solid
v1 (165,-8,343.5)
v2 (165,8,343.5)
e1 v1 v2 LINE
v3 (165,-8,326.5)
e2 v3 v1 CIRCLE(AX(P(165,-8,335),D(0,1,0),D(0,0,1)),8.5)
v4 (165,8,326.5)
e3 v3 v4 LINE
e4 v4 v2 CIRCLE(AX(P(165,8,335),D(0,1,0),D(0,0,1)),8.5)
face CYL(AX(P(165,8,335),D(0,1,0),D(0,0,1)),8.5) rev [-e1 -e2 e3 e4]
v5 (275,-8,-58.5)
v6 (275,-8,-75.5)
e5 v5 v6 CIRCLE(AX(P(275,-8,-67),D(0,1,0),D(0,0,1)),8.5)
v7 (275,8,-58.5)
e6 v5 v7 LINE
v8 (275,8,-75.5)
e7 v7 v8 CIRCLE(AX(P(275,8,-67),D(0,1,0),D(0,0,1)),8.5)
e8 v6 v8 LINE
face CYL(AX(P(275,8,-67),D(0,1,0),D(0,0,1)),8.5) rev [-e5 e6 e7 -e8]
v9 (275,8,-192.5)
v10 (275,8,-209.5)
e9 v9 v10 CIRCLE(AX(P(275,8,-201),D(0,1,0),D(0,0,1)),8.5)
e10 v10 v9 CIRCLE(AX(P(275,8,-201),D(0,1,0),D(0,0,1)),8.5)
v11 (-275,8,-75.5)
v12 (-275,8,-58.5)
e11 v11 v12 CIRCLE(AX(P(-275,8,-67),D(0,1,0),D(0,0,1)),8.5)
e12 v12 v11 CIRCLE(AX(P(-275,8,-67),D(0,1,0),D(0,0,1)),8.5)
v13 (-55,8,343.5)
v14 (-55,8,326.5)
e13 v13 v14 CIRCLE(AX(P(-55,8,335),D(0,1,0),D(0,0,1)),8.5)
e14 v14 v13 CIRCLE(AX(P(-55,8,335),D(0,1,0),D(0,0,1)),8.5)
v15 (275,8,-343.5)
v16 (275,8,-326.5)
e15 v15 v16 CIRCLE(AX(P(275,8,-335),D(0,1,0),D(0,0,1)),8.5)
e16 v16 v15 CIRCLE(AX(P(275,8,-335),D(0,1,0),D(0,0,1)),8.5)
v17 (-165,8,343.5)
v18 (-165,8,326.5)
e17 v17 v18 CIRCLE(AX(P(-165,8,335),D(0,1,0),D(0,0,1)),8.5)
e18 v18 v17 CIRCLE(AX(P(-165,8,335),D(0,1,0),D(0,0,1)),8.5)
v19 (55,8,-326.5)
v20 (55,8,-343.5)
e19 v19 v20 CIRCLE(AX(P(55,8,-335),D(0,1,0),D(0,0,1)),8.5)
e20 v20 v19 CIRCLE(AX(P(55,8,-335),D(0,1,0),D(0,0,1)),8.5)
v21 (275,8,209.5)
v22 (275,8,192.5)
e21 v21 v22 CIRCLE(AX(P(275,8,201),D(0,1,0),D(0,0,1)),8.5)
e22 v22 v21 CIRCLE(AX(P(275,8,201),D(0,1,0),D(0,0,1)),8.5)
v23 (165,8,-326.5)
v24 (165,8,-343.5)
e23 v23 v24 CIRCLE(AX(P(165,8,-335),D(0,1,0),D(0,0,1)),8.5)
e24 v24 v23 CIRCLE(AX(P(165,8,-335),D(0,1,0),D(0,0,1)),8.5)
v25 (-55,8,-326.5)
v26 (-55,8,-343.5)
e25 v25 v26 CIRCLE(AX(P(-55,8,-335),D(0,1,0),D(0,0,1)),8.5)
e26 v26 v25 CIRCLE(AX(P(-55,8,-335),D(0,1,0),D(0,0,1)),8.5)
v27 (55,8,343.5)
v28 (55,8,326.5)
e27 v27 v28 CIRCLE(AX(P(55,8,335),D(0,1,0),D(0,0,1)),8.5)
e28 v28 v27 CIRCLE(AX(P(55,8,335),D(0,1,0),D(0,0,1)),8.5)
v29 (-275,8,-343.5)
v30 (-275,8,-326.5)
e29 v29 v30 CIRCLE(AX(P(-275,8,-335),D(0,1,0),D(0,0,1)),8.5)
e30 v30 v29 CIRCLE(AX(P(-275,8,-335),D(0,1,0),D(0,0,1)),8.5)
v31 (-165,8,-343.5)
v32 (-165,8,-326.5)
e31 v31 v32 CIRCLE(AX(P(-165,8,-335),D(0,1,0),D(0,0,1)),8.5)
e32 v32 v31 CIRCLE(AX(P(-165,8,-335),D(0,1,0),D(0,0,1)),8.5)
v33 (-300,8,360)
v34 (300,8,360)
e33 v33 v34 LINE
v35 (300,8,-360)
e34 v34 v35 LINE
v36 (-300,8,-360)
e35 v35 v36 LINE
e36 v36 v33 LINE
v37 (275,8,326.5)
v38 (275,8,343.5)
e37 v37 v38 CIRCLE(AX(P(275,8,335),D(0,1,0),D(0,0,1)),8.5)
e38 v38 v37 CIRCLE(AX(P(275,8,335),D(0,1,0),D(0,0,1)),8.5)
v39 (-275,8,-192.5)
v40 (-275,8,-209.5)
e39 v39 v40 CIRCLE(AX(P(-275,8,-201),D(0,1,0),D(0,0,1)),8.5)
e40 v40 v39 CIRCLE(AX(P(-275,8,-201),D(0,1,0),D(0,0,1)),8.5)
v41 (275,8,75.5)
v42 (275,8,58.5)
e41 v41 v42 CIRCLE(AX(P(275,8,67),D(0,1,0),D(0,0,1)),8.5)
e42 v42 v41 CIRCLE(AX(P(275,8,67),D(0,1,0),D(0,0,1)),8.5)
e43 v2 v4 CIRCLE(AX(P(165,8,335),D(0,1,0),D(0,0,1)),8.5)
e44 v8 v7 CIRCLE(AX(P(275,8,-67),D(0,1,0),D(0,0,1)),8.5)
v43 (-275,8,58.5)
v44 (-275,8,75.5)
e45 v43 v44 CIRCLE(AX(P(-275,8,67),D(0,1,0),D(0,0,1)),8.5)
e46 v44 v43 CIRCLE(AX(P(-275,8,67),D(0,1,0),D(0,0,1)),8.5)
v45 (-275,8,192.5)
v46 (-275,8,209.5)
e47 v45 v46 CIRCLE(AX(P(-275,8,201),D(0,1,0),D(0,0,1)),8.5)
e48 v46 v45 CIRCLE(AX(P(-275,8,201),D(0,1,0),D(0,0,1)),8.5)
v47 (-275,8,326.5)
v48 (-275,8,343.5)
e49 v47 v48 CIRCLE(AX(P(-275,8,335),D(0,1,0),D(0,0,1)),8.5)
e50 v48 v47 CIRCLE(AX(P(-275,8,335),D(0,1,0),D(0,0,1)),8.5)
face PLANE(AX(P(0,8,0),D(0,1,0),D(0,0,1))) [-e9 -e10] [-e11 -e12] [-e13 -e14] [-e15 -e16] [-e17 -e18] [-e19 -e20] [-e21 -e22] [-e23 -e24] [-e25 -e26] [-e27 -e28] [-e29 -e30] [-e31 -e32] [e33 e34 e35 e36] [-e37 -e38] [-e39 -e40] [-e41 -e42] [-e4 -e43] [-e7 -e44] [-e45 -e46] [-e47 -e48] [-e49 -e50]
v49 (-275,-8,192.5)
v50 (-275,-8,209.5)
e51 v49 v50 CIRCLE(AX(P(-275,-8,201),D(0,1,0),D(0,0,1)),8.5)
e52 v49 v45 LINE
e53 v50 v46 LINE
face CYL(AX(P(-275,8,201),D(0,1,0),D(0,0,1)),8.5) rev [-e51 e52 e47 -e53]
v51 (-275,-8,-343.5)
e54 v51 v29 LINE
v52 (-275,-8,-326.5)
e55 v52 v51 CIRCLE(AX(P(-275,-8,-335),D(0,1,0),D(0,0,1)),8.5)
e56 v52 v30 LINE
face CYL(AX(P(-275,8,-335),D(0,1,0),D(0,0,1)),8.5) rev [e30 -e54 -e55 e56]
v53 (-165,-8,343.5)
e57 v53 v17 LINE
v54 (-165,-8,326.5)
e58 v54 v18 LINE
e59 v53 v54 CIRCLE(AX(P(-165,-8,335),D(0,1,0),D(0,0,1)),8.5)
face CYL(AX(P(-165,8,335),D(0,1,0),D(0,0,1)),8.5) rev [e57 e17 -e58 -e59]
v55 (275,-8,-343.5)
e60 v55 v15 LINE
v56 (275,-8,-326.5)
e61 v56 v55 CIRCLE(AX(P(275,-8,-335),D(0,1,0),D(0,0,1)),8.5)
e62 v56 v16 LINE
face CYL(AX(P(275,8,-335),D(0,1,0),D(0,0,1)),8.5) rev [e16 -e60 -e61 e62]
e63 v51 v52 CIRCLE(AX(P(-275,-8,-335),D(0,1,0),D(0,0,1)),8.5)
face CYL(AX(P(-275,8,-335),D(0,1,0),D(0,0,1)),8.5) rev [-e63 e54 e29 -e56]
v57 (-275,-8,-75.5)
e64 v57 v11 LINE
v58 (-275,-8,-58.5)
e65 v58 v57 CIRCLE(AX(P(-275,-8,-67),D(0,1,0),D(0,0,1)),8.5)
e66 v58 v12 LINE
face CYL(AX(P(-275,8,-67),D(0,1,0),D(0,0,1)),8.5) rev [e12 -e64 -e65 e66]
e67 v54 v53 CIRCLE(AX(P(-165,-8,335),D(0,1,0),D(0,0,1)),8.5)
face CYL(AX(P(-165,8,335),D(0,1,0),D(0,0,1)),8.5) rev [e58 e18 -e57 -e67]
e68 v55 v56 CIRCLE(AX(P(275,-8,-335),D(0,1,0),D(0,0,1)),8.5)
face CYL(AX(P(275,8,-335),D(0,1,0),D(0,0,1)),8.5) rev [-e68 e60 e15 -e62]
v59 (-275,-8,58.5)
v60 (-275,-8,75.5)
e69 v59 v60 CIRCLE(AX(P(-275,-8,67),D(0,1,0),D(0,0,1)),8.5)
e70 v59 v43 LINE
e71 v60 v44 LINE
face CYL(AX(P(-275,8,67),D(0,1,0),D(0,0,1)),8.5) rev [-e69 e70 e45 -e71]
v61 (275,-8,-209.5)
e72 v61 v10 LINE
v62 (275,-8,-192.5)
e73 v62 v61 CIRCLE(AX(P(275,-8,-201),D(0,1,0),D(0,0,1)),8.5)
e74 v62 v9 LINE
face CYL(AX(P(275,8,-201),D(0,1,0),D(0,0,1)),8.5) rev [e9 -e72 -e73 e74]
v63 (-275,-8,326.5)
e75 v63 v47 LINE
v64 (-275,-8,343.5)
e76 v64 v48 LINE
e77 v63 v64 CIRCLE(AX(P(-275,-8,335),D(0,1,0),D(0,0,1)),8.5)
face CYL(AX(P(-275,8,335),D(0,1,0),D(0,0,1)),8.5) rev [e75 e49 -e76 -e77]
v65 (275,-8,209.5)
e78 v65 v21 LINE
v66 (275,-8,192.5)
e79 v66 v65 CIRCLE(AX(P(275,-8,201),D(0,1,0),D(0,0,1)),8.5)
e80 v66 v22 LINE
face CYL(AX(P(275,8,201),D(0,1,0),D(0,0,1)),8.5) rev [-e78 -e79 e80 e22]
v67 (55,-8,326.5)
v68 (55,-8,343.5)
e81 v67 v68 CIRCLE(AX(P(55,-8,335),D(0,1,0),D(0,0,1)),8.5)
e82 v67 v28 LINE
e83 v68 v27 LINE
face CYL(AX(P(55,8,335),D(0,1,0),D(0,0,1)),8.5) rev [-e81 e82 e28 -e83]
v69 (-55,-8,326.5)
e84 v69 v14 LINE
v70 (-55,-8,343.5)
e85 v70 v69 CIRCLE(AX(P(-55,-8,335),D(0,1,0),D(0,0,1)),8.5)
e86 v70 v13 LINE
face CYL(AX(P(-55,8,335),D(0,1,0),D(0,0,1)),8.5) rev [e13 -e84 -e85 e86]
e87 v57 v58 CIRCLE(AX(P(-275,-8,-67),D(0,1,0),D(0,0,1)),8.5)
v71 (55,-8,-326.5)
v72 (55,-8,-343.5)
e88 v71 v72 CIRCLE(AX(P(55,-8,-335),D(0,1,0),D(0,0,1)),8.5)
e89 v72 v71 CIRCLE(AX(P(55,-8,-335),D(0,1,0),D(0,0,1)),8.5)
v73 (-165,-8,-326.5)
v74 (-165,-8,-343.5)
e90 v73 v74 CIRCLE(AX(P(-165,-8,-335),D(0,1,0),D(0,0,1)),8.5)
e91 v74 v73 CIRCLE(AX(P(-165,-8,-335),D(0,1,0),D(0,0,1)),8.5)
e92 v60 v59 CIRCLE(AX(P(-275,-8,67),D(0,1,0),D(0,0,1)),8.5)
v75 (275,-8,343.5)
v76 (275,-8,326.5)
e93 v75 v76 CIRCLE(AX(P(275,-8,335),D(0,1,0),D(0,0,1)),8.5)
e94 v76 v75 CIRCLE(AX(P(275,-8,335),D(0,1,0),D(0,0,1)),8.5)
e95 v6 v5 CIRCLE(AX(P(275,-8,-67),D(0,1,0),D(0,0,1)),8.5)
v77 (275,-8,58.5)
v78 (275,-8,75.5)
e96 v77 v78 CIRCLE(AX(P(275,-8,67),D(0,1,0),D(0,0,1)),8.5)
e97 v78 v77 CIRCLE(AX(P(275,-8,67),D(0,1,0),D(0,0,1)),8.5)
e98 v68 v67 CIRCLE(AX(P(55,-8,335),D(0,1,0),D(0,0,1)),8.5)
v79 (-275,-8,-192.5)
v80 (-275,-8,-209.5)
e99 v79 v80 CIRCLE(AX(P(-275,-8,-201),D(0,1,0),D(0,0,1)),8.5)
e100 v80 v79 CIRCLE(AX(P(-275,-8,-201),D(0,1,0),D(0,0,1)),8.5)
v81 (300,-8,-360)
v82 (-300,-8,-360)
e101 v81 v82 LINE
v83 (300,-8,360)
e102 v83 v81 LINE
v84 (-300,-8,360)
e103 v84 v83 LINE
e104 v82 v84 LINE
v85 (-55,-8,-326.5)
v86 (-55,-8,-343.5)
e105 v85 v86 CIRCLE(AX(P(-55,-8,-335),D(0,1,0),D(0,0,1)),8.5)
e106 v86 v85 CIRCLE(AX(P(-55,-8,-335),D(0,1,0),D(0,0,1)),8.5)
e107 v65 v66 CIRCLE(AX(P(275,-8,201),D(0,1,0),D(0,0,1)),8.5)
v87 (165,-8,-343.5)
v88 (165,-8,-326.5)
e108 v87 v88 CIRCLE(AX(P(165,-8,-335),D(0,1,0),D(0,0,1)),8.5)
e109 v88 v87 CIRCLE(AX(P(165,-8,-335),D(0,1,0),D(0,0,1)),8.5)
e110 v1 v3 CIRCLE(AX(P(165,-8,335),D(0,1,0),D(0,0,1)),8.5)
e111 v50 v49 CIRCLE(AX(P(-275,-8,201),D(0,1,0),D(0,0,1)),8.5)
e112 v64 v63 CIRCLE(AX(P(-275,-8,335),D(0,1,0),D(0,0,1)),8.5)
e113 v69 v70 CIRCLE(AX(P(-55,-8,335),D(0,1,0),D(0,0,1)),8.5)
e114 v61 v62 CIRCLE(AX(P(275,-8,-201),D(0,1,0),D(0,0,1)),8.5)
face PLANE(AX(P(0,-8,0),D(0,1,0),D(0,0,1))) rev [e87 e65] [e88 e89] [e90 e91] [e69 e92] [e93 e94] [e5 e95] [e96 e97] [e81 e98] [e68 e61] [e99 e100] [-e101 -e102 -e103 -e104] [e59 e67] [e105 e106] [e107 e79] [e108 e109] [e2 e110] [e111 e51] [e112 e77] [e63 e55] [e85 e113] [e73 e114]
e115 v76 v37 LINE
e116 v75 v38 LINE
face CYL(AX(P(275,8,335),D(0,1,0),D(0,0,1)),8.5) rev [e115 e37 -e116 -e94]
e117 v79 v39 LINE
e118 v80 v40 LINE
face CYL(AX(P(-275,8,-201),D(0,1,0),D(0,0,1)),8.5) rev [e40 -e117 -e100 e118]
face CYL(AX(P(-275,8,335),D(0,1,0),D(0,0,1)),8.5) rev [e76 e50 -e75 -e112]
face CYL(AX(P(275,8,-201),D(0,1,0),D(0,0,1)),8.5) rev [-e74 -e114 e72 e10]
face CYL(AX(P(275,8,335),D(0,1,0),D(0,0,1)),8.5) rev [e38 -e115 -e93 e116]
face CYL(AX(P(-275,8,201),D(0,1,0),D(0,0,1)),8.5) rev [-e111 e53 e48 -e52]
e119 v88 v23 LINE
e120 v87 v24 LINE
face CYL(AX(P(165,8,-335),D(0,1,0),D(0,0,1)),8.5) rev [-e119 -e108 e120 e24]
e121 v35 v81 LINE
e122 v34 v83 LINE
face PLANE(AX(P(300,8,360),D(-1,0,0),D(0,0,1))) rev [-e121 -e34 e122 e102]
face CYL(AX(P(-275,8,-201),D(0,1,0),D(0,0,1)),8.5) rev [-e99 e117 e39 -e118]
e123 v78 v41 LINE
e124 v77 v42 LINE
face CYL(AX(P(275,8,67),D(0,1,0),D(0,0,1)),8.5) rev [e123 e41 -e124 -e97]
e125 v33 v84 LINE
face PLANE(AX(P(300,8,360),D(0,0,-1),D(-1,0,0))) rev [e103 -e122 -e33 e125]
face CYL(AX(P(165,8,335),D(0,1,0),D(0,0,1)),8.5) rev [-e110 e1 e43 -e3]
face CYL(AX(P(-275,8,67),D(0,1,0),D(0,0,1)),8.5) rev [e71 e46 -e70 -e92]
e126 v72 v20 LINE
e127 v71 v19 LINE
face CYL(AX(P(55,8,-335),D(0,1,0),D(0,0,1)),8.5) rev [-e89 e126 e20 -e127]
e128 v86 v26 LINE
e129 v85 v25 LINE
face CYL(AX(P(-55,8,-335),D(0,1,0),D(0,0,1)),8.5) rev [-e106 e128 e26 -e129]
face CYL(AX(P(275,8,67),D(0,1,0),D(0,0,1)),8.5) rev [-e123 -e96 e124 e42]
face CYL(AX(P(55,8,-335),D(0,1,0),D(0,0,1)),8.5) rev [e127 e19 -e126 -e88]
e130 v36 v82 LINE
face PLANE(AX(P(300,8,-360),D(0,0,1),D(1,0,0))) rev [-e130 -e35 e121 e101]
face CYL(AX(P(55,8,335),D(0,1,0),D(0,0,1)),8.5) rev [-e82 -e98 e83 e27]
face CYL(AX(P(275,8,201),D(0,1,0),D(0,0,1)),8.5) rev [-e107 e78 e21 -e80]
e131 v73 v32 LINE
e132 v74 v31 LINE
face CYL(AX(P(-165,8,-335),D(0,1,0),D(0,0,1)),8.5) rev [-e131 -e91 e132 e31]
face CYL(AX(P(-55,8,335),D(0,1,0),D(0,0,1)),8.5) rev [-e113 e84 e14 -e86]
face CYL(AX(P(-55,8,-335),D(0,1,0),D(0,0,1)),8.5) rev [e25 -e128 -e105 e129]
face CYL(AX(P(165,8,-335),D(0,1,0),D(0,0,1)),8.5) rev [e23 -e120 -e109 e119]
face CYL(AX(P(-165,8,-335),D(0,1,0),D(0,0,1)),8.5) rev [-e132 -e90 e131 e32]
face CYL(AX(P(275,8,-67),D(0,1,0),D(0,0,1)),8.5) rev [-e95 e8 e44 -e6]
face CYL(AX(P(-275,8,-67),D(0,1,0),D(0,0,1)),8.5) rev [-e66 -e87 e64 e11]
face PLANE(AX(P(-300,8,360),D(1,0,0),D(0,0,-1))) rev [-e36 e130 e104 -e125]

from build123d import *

# Parameters (mm, degrees)
SKETCH1_W                  = 600
SKETCH1_H                  = 720
BOSS_EXTRUDE1_DEPTH        = 8
F_17_0_17_DIAMETER_HOLE1_D = 17


with BuildPart() as part:
    # Sketch1 → Boss-Extrude1 (new, symmetric)
    with BuildSketch(Plane(origin=(0, 0, 0), x_dir=(1, 0, 0), z_dir=(0, 1, 0))):
        Rectangle(SKETCH1_W, SKETCH1_H)
    extrude(amount=BOSS_EXTRUDE1_DEPTH, both=True)

    # Ø17.0 (17) Diameter Hole1 (through all)
    with Locations(Plane(origin=(0, 8, 0), x_dir=(1, 0, 0), z_dir=(0, 1, 0))):
        with Locations((-275, -335), (-165, -335), (-55, -335), (55, -335), (165, -335), (275, -335), (-275, -201), (-275, -67), (-275, 67), (-275, 201), (-275, 335), (275, 335), (165, 335), (55, 335), (-55, 335), (-165, 335), (275, 201), (275, 67), (275, -67), (275, -201)):
            Hole(F_17_0_17_DIAMETER_HOLE1_D / 2)


solid = part.part
